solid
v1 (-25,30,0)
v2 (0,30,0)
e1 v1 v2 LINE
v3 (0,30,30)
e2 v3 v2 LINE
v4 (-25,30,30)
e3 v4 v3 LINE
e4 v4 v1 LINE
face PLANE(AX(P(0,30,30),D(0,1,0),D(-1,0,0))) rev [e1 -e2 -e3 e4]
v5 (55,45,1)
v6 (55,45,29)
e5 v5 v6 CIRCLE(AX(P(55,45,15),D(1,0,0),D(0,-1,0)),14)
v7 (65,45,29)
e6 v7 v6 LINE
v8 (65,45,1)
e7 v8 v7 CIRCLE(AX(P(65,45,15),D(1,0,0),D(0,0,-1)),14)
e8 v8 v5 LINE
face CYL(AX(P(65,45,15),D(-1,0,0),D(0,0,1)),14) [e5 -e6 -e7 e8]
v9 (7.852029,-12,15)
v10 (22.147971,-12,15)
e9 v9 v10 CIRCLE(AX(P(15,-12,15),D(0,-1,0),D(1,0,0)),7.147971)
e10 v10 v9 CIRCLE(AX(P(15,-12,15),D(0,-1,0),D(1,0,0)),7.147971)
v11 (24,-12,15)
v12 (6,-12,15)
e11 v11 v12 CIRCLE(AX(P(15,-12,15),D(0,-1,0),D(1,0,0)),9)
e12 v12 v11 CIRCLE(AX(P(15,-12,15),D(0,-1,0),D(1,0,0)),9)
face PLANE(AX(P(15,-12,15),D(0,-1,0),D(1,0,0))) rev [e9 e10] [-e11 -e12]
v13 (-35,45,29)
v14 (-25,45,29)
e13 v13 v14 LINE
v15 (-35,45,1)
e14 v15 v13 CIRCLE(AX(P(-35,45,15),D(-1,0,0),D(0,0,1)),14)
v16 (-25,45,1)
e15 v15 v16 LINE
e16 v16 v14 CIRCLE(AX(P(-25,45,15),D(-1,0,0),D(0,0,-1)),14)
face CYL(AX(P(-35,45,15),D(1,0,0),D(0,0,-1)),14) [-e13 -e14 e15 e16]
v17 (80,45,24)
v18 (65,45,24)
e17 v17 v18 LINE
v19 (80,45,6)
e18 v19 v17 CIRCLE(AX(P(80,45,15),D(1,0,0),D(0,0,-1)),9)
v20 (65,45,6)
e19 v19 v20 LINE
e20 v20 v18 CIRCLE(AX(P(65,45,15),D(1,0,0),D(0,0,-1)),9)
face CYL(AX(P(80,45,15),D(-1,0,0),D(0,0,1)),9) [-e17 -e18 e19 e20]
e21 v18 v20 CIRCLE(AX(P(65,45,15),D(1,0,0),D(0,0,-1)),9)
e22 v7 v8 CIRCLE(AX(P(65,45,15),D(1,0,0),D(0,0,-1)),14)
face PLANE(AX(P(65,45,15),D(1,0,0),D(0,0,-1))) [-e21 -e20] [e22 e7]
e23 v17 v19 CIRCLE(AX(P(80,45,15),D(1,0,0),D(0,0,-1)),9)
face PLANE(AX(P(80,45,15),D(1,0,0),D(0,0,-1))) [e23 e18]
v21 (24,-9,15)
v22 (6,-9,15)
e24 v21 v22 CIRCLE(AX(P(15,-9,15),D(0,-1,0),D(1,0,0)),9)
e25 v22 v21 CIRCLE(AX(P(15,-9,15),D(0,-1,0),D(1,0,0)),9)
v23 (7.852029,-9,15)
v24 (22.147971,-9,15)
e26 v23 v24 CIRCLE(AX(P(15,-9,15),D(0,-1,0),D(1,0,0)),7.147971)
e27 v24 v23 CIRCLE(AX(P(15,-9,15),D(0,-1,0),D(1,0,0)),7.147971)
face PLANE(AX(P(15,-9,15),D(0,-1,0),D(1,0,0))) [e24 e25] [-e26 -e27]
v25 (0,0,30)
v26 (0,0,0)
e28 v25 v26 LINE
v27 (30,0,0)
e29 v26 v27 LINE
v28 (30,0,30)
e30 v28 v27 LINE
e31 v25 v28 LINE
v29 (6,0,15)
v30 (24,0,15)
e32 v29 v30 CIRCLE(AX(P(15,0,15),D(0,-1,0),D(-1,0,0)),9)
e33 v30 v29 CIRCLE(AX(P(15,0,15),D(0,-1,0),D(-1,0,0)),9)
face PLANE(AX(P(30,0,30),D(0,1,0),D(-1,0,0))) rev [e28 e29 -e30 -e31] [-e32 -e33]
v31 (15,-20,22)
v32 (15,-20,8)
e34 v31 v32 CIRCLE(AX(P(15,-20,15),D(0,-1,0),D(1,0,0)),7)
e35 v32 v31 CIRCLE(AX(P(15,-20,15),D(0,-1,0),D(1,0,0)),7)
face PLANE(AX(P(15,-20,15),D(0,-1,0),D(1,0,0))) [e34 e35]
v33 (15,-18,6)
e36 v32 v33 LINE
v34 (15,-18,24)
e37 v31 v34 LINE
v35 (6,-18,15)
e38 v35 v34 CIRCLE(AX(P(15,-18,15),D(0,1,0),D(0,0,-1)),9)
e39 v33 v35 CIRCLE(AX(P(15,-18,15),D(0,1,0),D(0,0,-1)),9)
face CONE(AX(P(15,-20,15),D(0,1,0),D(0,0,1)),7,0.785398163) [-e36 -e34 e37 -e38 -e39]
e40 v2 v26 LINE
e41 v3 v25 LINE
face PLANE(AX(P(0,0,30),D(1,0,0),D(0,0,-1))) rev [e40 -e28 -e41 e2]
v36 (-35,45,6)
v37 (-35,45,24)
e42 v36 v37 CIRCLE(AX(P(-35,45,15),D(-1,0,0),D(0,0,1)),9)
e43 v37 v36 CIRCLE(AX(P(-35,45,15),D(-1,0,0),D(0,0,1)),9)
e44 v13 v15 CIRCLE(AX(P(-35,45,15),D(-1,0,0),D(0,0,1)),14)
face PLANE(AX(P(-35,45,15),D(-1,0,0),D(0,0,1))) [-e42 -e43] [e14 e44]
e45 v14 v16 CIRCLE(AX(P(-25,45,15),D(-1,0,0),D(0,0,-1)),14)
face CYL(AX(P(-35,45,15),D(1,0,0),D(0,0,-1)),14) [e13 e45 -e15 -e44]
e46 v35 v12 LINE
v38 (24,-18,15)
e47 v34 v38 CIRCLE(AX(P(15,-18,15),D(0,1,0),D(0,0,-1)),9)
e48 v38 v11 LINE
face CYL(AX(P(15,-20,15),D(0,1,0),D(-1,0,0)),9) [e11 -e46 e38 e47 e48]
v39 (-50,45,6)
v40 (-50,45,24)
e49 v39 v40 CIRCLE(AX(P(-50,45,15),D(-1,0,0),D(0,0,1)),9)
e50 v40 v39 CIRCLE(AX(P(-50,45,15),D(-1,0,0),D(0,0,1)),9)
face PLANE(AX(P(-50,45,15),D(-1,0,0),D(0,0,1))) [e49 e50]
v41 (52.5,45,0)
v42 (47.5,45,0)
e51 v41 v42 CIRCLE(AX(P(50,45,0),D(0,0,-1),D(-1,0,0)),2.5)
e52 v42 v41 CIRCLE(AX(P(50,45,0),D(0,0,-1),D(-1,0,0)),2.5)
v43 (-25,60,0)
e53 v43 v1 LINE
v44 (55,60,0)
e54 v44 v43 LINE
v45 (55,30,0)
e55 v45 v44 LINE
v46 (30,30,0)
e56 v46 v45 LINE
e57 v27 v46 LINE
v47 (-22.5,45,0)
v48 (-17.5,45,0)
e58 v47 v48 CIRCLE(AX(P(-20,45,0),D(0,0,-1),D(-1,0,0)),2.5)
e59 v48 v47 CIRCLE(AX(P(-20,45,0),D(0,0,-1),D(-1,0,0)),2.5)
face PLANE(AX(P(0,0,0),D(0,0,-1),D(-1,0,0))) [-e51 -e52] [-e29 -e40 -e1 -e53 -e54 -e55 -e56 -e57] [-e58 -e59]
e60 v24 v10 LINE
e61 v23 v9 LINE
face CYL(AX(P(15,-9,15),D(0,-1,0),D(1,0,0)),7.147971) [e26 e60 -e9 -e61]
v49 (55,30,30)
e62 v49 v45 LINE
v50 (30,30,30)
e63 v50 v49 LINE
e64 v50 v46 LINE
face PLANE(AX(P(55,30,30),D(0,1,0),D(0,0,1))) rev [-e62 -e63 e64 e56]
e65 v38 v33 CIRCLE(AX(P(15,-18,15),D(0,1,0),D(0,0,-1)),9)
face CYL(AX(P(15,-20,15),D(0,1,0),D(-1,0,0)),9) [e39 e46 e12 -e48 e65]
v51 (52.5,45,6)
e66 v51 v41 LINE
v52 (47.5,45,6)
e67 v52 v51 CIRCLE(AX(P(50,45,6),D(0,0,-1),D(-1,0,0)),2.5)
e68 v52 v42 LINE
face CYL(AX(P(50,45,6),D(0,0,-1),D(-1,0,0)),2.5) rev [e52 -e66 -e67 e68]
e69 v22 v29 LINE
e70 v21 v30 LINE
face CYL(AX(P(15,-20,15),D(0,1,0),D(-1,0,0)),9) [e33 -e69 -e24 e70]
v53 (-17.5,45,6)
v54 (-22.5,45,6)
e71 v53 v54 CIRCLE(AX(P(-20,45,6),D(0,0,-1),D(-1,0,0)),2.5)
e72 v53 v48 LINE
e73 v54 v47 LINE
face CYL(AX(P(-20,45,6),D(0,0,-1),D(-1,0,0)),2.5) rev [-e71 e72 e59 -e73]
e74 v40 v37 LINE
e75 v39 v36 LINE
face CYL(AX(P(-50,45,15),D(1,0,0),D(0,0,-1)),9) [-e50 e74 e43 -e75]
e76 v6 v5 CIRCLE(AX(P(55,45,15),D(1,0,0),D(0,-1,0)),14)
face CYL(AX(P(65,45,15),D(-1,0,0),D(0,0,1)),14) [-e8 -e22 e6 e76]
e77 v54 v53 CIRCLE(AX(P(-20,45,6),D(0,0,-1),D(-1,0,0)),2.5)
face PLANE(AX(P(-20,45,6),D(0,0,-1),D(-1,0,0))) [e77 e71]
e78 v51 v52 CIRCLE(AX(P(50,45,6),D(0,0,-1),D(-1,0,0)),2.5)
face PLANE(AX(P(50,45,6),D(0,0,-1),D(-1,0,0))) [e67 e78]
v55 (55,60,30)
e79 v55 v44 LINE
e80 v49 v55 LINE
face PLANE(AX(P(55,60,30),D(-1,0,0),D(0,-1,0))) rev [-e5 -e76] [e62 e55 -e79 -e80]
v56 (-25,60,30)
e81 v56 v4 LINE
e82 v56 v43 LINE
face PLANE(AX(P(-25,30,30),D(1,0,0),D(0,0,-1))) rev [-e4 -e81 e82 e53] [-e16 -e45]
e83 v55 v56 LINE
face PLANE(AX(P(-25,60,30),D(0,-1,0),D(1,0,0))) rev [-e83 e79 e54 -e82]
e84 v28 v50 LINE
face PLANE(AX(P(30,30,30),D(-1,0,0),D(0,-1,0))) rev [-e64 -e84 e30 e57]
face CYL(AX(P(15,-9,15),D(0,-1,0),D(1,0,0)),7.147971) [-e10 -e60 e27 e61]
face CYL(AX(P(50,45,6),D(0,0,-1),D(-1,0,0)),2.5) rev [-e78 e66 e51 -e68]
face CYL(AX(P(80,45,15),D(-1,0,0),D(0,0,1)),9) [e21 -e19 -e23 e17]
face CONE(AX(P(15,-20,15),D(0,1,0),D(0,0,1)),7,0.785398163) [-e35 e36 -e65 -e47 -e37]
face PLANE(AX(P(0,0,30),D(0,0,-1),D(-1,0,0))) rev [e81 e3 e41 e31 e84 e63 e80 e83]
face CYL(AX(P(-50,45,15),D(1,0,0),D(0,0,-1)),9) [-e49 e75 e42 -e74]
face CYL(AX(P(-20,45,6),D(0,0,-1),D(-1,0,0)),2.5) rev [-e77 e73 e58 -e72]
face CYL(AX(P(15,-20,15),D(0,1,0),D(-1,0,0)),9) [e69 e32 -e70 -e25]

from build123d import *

# Parameters (mm, degrees)
BOSS_EXTRUDE1_DEPTH = 30
SKETCH2_R           = 14
BOSS_EXTRUDE2_DEPTH = 10
SKETCH3_R           = 9
BOSS_EXTRUDE3_DEPTH = 15
BOSS_EXTRUDE4_START = 10
SKETCH4_R           = 14
BOSS_EXTRUDE4_DEPTH = 10
BOSS_EXTRUDE5_START = 15
SKETCH5_R           = 9
BOSS_EXTRUDE5_DEPTH = 15
SKETCH6_R           = 9
BOSS_EXTRUDE6_DEPTH = 20
CUT_EXTRUDE1_START  = -8
SKETCH7_R           = 10.265478639
SKETCH7_R_2         = 7.147971295
CUT_EXTRUDE1_DEPTH  = 3
CHAMFER1_SIZE       = 2
SKETCH8_R           = 2.5
CUT_EXTRUDE2_DEPTH  = 6


with BuildPart() as part:
    # Sketch1 → Boss-Extrude1 (new body)
    with BuildSketch(Plane.XY):
        Polygon((0, 0), (0, 30), (-25, 30), (-25, 60), (55, 60), (55, 30), (30, 30), (30, 0), align=None)
    extrude(amount=BOSS_EXTRUDE1_DEPTH)

    # Sketch2 → Boss-Extrude2 (add)
    with BuildSketch(Plane(origin=(55, 0, 0), x_dir=(0, 0, -1), z_dir=(1, 0, 0))):
        with Locations(Location((-15, 45, 0), (0, 0, 270))):
            Circle(SKETCH2_R)
    extrude(amount=BOSS_EXTRUDE2_DEPTH)

    # Sketch3 → Boss-Extrude3 (add)
    with BuildSketch(Plane(origin=(65, 0, 0), x_dir=(0, 0, -1), z_dir=(1, 0, 0))):
        with Locations((-15, 45)):
            Circle(SKETCH3_R)
    extrude(amount=BOSS_EXTRUDE3_DEPTH)

    # Sketch4 → Boss-Extrude4 (add)
    with BuildSketch(Plane.ZY.offset(25).offset(BOSS_EXTRUDE4_START)):
        with Locations(Location((15, 45, 0), (0, 0, 270))):
            Circle(SKETCH4_R)
    extrude(amount=-BOSS_EXTRUDE4_DEPTH)

    # Sketch5 → Boss-Extrude5 (add)
    with BuildSketch(Plane.ZY.offset(35).offset(BOSS_EXTRUDE5_START)):
        with Locations(Location((15, 45, 0), (0, 0, 180))):
            Circle(SKETCH5_R)
    extrude(amount=-BOSS_EXTRUDE5_DEPTH)

    # Sketch6 → Boss-Extrude6 (add)
    with BuildSketch(Plane(origin=(0, 0, 0), x_dir=(-1, 0, 0), z_dir=(0, -1, 0))):
        with Locations((-15, -15)):
            Circle(SKETCH6_R)
    extrude(amount=BOSS_EXTRUDE6_DEPTH)

    # Sketch7 → Cut-Extrude1 (cut)
    with BuildSketch(Plane(origin=(0, -20, 0), x_dir=(-1, 0, 0), z_dir=(0, -1, 0)).offset(CUT_EXTRUDE1_START)):
        with Locations((-15, -15)):
            Circle(SKETCH7_R)
        with Locations(Location((-15, -15, 0), (0, 0, 180))):
            Circle(SKETCH7_R_2, mode=Mode.SUBTRACT)
    extrude(amount=-CUT_EXTRUDE1_DEPTH, mode=Mode.SUBTRACT)

    # Chamfer1
    chamfer1_edges = [part.edges().sort_by_distance(p)[0] for p in [
        (24, -20, 15),
    ]]
    chamfer(chamfer1_edges, length=CHAMFER1_SIZE)

    # Sketch8 → Cut-Extrude2 (cut)
    with BuildSketch(Plane(origin=(0, 0, 0), x_dir=(-1, 0, 0), z_dir=(0, 0, -1))):
        with Locations((-50, 45)):
            Circle(SKETCH8_R)
        with Locations((20, 45)):
            Circle(SKETCH8_R)
    extrude(amount=-CUT_EXTRUDE2_DEPTH, mode=Mode.SUBTRACT)


solid = part.part
